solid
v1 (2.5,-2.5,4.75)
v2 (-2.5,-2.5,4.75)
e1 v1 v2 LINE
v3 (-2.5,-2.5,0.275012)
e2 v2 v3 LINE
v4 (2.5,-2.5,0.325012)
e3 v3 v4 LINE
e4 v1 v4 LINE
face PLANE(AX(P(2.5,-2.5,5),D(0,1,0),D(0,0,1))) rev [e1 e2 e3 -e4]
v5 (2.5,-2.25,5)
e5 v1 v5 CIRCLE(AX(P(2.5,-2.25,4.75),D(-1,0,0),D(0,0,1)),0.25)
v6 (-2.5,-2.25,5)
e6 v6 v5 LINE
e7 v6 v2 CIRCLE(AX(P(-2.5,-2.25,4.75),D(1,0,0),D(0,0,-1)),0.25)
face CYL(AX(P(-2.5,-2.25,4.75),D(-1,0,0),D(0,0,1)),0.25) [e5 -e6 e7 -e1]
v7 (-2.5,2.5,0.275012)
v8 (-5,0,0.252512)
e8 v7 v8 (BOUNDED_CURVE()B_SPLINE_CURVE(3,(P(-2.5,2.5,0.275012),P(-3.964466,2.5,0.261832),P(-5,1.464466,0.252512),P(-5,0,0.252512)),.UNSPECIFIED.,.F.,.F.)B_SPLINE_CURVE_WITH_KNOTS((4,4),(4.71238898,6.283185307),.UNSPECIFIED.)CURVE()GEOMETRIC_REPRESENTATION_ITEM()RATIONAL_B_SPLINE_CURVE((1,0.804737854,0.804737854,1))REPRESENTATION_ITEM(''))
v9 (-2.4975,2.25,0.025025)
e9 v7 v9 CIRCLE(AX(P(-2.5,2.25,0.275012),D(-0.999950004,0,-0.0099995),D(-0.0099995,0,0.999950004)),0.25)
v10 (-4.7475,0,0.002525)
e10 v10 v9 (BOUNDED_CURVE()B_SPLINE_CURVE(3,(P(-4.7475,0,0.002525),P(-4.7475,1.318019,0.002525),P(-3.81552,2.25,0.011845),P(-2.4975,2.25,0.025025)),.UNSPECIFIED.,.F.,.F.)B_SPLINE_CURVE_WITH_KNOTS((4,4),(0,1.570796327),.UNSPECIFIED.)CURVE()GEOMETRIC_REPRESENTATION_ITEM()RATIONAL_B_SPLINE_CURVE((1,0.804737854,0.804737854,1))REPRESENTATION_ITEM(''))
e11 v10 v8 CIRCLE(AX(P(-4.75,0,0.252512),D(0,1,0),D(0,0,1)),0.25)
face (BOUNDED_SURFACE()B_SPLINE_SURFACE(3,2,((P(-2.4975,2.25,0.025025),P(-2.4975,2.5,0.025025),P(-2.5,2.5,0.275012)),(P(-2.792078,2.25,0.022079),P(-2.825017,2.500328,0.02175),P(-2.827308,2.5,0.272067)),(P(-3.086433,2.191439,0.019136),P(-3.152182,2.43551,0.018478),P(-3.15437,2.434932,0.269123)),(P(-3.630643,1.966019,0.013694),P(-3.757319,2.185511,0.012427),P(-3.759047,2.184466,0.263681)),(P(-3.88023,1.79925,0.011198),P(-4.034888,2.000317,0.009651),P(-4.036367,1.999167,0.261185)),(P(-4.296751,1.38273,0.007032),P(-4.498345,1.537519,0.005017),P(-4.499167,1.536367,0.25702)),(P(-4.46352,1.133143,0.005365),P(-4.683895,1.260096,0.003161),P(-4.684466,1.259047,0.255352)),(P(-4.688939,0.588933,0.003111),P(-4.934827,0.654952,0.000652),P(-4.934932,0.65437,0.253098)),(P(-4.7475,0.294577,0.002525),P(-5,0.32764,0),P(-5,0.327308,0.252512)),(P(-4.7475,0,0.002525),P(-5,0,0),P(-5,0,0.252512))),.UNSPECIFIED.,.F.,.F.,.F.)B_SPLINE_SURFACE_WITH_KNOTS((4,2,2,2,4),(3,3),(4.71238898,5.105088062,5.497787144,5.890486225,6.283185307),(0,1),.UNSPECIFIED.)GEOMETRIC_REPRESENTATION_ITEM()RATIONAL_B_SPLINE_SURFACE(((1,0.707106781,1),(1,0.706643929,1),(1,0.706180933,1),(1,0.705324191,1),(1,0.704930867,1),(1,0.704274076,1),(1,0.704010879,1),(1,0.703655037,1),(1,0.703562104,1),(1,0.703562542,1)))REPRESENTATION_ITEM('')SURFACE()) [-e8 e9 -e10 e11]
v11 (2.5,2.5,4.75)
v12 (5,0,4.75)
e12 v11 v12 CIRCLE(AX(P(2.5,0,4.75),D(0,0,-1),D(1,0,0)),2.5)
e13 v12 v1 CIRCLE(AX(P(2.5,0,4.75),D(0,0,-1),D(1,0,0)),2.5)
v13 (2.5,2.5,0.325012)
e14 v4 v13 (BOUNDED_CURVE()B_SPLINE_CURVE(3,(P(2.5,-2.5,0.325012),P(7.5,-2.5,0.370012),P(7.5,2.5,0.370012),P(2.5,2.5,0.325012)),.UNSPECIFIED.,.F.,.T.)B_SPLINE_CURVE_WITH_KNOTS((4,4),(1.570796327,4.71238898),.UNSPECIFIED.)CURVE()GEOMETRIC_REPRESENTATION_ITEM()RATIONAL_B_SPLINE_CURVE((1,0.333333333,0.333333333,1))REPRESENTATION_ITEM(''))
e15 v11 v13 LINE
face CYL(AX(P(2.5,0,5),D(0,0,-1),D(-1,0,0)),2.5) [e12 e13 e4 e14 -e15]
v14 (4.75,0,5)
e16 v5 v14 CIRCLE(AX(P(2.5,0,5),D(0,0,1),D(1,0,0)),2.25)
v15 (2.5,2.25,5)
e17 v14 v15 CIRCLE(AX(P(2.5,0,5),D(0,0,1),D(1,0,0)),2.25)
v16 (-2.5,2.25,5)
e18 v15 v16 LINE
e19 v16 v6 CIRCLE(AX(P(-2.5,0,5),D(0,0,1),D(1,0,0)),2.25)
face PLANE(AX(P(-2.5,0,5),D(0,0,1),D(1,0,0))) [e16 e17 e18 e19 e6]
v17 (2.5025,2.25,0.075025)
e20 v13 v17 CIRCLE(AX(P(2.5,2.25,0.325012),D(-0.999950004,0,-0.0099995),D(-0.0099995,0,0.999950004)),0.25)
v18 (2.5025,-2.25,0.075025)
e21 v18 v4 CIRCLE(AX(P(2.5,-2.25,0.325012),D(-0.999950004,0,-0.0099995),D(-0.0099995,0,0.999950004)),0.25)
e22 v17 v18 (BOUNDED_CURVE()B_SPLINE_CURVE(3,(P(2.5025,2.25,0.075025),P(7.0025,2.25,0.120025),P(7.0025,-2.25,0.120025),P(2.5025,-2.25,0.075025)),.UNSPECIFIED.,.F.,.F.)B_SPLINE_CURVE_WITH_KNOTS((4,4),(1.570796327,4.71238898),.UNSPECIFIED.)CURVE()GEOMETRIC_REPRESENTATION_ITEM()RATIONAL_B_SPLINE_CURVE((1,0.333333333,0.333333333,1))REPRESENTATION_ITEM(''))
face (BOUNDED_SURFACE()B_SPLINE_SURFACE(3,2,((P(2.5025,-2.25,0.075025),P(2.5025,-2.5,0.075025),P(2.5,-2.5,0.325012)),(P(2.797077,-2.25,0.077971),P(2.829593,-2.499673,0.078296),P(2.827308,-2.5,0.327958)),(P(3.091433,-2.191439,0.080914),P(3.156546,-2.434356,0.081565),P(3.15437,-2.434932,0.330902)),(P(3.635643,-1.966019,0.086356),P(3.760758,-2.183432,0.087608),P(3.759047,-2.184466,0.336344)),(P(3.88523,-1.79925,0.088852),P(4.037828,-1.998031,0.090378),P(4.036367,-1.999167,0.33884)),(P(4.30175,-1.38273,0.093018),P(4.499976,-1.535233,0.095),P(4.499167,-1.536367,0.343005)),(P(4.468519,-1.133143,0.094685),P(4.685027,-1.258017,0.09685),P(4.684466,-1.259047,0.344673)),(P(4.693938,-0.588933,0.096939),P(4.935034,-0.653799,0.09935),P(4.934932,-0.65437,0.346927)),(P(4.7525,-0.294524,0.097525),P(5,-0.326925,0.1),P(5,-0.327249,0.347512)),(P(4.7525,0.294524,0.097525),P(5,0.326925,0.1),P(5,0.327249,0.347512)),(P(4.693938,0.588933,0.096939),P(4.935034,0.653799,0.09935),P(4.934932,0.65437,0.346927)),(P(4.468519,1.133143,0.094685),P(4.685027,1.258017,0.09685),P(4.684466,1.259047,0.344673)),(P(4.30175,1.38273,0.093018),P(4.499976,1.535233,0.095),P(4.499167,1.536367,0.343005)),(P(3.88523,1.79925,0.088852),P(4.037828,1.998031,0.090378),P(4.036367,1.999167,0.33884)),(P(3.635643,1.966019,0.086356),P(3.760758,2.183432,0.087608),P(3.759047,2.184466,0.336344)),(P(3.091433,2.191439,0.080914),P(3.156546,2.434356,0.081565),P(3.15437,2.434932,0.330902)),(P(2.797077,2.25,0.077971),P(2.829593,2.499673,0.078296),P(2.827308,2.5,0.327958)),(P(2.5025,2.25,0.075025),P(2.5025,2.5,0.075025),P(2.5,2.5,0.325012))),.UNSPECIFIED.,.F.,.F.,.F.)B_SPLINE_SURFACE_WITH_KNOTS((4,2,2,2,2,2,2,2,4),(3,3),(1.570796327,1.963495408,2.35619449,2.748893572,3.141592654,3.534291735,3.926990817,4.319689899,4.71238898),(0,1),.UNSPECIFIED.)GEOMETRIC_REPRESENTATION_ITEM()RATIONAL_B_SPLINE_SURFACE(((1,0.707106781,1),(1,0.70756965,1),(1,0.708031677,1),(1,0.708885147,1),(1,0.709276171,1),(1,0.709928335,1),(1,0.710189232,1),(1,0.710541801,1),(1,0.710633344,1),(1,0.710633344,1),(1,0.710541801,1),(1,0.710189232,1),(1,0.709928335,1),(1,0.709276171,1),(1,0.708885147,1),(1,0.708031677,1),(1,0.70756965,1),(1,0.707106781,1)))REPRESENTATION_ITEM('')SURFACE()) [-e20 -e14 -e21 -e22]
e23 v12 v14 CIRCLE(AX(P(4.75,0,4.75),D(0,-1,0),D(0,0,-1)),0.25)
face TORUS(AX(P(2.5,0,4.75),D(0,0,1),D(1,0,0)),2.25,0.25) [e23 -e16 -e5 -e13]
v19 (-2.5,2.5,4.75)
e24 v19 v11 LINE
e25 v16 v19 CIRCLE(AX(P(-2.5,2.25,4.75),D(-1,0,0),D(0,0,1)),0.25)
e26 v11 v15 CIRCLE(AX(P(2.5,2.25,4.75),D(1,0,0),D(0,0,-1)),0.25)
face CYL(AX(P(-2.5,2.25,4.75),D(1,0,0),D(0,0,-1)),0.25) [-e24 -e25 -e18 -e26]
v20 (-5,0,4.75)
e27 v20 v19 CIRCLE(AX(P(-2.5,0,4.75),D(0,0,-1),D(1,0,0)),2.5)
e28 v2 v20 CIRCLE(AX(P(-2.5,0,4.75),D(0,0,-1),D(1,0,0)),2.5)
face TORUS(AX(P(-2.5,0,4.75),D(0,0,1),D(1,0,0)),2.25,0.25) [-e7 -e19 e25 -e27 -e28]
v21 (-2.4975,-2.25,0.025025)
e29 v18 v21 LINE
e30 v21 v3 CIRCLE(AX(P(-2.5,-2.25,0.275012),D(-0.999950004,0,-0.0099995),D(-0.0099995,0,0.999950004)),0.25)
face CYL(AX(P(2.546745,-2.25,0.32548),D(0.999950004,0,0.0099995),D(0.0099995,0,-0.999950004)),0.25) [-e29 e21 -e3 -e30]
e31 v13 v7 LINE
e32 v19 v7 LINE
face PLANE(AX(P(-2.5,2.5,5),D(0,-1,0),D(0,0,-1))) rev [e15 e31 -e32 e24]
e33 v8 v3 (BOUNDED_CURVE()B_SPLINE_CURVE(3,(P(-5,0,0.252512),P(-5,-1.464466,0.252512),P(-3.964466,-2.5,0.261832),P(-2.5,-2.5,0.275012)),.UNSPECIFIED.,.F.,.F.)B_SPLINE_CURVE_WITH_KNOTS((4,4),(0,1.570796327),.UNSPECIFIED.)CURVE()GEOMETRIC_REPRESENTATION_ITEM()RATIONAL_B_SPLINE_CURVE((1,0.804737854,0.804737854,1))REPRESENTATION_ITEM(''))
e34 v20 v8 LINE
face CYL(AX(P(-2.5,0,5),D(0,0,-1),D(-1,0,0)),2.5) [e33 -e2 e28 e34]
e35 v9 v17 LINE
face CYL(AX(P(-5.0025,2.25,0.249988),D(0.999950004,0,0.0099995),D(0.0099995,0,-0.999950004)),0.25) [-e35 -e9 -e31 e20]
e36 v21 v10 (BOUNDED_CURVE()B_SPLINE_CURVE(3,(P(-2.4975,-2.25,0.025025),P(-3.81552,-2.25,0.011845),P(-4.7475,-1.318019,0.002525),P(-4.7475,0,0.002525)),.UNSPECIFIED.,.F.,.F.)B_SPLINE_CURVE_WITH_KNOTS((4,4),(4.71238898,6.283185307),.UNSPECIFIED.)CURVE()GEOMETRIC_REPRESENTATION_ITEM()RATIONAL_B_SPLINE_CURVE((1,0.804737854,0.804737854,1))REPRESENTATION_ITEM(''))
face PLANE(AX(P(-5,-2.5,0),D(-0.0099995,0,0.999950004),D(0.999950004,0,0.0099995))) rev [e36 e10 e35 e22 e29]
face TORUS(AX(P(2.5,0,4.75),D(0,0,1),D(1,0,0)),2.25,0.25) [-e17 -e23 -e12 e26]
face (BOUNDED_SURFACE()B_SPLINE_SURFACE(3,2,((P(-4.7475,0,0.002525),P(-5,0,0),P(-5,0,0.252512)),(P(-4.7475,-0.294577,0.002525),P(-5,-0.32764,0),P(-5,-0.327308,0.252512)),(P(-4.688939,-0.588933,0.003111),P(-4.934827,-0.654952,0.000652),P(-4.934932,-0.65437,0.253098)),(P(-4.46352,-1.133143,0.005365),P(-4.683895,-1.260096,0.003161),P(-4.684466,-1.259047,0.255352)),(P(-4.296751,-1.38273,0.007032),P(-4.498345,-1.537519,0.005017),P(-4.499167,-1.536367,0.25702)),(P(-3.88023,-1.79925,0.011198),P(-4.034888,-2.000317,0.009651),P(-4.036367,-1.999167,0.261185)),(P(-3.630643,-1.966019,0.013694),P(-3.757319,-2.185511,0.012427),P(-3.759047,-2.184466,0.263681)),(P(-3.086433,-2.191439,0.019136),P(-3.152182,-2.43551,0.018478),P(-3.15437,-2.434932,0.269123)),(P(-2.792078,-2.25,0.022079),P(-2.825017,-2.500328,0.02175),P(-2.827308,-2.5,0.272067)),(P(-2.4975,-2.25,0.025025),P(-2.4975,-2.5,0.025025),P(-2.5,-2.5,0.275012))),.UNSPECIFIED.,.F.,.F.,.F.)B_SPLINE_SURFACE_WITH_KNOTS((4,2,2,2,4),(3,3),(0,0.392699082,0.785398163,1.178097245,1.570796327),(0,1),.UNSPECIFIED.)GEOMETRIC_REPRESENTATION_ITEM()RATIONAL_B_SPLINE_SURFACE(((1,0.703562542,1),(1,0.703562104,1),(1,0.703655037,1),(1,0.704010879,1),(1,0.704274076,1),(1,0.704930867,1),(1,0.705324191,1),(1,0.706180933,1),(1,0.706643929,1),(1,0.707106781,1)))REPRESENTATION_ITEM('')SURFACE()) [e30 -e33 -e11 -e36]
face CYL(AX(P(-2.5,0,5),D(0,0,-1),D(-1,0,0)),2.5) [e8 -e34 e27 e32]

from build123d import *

# Parameters (mm, degrees)
EXTRUDE1_DEPTH          = 5
CUT_EXTRUDE1_DEPTH      = 8.5
CUT_EXTRUDE1_DEPTH_BACK = 8.5
FILLET2_R               = 0.25


with BuildPart() as part:
    # Sketch1 → Extrude1 (new body)
    with BuildSketch(Plane.XY):
        with BuildLine():
            Line((-2.5, 2.5), (2.5, 2.5))
            ThreePointArc((2.5, 2.5), (5, 0), (2.5, -2.5))
            Line((2.5, -2.5), (-2.5, -2.5))
            ThreePointArc((-2.5, -2.5), (-5, 0), (-2.5, 2.5))
        make_face()
    extrude(amount=EXTRUDE1_DEPTH)

    # Sketch2 → Cut-Extrude1 (cut, two sides: drawn at the far end of the back side and taken through both)
    with BuildSketch(Plane(origin=(0, 0, 0), x_dir=(1, 0, 0), z_dir=(0, 1, 0)).offset(-CUT_EXTRUDE1_DEPTH_BACK)):
        Polygon((-5, 0), (5, 0), (5, -0.1), align=None)
    extrude(amount=CUT_EXTRUDE1_DEPTH + CUT_EXTRUDE1_DEPTH_BACK, mode=Mode.SUBTRACT)

    # Fillet2
    fillet2_edges = [part.edges().sort_by_distance(p)[0] for p in [
        (5, 0, 5),
        (0, 2.5, 5),
        (-4.267744857, -1.767789049, 0.007322551),
        (0, -2.5, 0.05),
        (4.267744857, -1.767789049, 0.092677449),
        (0, 2.5, 0.05),
        (-5, 0, 5),
        (0, -2.5, 5),
    ]]
    fillet(fillet2_edges, radius=FILLET2_R)


solid = part.part
